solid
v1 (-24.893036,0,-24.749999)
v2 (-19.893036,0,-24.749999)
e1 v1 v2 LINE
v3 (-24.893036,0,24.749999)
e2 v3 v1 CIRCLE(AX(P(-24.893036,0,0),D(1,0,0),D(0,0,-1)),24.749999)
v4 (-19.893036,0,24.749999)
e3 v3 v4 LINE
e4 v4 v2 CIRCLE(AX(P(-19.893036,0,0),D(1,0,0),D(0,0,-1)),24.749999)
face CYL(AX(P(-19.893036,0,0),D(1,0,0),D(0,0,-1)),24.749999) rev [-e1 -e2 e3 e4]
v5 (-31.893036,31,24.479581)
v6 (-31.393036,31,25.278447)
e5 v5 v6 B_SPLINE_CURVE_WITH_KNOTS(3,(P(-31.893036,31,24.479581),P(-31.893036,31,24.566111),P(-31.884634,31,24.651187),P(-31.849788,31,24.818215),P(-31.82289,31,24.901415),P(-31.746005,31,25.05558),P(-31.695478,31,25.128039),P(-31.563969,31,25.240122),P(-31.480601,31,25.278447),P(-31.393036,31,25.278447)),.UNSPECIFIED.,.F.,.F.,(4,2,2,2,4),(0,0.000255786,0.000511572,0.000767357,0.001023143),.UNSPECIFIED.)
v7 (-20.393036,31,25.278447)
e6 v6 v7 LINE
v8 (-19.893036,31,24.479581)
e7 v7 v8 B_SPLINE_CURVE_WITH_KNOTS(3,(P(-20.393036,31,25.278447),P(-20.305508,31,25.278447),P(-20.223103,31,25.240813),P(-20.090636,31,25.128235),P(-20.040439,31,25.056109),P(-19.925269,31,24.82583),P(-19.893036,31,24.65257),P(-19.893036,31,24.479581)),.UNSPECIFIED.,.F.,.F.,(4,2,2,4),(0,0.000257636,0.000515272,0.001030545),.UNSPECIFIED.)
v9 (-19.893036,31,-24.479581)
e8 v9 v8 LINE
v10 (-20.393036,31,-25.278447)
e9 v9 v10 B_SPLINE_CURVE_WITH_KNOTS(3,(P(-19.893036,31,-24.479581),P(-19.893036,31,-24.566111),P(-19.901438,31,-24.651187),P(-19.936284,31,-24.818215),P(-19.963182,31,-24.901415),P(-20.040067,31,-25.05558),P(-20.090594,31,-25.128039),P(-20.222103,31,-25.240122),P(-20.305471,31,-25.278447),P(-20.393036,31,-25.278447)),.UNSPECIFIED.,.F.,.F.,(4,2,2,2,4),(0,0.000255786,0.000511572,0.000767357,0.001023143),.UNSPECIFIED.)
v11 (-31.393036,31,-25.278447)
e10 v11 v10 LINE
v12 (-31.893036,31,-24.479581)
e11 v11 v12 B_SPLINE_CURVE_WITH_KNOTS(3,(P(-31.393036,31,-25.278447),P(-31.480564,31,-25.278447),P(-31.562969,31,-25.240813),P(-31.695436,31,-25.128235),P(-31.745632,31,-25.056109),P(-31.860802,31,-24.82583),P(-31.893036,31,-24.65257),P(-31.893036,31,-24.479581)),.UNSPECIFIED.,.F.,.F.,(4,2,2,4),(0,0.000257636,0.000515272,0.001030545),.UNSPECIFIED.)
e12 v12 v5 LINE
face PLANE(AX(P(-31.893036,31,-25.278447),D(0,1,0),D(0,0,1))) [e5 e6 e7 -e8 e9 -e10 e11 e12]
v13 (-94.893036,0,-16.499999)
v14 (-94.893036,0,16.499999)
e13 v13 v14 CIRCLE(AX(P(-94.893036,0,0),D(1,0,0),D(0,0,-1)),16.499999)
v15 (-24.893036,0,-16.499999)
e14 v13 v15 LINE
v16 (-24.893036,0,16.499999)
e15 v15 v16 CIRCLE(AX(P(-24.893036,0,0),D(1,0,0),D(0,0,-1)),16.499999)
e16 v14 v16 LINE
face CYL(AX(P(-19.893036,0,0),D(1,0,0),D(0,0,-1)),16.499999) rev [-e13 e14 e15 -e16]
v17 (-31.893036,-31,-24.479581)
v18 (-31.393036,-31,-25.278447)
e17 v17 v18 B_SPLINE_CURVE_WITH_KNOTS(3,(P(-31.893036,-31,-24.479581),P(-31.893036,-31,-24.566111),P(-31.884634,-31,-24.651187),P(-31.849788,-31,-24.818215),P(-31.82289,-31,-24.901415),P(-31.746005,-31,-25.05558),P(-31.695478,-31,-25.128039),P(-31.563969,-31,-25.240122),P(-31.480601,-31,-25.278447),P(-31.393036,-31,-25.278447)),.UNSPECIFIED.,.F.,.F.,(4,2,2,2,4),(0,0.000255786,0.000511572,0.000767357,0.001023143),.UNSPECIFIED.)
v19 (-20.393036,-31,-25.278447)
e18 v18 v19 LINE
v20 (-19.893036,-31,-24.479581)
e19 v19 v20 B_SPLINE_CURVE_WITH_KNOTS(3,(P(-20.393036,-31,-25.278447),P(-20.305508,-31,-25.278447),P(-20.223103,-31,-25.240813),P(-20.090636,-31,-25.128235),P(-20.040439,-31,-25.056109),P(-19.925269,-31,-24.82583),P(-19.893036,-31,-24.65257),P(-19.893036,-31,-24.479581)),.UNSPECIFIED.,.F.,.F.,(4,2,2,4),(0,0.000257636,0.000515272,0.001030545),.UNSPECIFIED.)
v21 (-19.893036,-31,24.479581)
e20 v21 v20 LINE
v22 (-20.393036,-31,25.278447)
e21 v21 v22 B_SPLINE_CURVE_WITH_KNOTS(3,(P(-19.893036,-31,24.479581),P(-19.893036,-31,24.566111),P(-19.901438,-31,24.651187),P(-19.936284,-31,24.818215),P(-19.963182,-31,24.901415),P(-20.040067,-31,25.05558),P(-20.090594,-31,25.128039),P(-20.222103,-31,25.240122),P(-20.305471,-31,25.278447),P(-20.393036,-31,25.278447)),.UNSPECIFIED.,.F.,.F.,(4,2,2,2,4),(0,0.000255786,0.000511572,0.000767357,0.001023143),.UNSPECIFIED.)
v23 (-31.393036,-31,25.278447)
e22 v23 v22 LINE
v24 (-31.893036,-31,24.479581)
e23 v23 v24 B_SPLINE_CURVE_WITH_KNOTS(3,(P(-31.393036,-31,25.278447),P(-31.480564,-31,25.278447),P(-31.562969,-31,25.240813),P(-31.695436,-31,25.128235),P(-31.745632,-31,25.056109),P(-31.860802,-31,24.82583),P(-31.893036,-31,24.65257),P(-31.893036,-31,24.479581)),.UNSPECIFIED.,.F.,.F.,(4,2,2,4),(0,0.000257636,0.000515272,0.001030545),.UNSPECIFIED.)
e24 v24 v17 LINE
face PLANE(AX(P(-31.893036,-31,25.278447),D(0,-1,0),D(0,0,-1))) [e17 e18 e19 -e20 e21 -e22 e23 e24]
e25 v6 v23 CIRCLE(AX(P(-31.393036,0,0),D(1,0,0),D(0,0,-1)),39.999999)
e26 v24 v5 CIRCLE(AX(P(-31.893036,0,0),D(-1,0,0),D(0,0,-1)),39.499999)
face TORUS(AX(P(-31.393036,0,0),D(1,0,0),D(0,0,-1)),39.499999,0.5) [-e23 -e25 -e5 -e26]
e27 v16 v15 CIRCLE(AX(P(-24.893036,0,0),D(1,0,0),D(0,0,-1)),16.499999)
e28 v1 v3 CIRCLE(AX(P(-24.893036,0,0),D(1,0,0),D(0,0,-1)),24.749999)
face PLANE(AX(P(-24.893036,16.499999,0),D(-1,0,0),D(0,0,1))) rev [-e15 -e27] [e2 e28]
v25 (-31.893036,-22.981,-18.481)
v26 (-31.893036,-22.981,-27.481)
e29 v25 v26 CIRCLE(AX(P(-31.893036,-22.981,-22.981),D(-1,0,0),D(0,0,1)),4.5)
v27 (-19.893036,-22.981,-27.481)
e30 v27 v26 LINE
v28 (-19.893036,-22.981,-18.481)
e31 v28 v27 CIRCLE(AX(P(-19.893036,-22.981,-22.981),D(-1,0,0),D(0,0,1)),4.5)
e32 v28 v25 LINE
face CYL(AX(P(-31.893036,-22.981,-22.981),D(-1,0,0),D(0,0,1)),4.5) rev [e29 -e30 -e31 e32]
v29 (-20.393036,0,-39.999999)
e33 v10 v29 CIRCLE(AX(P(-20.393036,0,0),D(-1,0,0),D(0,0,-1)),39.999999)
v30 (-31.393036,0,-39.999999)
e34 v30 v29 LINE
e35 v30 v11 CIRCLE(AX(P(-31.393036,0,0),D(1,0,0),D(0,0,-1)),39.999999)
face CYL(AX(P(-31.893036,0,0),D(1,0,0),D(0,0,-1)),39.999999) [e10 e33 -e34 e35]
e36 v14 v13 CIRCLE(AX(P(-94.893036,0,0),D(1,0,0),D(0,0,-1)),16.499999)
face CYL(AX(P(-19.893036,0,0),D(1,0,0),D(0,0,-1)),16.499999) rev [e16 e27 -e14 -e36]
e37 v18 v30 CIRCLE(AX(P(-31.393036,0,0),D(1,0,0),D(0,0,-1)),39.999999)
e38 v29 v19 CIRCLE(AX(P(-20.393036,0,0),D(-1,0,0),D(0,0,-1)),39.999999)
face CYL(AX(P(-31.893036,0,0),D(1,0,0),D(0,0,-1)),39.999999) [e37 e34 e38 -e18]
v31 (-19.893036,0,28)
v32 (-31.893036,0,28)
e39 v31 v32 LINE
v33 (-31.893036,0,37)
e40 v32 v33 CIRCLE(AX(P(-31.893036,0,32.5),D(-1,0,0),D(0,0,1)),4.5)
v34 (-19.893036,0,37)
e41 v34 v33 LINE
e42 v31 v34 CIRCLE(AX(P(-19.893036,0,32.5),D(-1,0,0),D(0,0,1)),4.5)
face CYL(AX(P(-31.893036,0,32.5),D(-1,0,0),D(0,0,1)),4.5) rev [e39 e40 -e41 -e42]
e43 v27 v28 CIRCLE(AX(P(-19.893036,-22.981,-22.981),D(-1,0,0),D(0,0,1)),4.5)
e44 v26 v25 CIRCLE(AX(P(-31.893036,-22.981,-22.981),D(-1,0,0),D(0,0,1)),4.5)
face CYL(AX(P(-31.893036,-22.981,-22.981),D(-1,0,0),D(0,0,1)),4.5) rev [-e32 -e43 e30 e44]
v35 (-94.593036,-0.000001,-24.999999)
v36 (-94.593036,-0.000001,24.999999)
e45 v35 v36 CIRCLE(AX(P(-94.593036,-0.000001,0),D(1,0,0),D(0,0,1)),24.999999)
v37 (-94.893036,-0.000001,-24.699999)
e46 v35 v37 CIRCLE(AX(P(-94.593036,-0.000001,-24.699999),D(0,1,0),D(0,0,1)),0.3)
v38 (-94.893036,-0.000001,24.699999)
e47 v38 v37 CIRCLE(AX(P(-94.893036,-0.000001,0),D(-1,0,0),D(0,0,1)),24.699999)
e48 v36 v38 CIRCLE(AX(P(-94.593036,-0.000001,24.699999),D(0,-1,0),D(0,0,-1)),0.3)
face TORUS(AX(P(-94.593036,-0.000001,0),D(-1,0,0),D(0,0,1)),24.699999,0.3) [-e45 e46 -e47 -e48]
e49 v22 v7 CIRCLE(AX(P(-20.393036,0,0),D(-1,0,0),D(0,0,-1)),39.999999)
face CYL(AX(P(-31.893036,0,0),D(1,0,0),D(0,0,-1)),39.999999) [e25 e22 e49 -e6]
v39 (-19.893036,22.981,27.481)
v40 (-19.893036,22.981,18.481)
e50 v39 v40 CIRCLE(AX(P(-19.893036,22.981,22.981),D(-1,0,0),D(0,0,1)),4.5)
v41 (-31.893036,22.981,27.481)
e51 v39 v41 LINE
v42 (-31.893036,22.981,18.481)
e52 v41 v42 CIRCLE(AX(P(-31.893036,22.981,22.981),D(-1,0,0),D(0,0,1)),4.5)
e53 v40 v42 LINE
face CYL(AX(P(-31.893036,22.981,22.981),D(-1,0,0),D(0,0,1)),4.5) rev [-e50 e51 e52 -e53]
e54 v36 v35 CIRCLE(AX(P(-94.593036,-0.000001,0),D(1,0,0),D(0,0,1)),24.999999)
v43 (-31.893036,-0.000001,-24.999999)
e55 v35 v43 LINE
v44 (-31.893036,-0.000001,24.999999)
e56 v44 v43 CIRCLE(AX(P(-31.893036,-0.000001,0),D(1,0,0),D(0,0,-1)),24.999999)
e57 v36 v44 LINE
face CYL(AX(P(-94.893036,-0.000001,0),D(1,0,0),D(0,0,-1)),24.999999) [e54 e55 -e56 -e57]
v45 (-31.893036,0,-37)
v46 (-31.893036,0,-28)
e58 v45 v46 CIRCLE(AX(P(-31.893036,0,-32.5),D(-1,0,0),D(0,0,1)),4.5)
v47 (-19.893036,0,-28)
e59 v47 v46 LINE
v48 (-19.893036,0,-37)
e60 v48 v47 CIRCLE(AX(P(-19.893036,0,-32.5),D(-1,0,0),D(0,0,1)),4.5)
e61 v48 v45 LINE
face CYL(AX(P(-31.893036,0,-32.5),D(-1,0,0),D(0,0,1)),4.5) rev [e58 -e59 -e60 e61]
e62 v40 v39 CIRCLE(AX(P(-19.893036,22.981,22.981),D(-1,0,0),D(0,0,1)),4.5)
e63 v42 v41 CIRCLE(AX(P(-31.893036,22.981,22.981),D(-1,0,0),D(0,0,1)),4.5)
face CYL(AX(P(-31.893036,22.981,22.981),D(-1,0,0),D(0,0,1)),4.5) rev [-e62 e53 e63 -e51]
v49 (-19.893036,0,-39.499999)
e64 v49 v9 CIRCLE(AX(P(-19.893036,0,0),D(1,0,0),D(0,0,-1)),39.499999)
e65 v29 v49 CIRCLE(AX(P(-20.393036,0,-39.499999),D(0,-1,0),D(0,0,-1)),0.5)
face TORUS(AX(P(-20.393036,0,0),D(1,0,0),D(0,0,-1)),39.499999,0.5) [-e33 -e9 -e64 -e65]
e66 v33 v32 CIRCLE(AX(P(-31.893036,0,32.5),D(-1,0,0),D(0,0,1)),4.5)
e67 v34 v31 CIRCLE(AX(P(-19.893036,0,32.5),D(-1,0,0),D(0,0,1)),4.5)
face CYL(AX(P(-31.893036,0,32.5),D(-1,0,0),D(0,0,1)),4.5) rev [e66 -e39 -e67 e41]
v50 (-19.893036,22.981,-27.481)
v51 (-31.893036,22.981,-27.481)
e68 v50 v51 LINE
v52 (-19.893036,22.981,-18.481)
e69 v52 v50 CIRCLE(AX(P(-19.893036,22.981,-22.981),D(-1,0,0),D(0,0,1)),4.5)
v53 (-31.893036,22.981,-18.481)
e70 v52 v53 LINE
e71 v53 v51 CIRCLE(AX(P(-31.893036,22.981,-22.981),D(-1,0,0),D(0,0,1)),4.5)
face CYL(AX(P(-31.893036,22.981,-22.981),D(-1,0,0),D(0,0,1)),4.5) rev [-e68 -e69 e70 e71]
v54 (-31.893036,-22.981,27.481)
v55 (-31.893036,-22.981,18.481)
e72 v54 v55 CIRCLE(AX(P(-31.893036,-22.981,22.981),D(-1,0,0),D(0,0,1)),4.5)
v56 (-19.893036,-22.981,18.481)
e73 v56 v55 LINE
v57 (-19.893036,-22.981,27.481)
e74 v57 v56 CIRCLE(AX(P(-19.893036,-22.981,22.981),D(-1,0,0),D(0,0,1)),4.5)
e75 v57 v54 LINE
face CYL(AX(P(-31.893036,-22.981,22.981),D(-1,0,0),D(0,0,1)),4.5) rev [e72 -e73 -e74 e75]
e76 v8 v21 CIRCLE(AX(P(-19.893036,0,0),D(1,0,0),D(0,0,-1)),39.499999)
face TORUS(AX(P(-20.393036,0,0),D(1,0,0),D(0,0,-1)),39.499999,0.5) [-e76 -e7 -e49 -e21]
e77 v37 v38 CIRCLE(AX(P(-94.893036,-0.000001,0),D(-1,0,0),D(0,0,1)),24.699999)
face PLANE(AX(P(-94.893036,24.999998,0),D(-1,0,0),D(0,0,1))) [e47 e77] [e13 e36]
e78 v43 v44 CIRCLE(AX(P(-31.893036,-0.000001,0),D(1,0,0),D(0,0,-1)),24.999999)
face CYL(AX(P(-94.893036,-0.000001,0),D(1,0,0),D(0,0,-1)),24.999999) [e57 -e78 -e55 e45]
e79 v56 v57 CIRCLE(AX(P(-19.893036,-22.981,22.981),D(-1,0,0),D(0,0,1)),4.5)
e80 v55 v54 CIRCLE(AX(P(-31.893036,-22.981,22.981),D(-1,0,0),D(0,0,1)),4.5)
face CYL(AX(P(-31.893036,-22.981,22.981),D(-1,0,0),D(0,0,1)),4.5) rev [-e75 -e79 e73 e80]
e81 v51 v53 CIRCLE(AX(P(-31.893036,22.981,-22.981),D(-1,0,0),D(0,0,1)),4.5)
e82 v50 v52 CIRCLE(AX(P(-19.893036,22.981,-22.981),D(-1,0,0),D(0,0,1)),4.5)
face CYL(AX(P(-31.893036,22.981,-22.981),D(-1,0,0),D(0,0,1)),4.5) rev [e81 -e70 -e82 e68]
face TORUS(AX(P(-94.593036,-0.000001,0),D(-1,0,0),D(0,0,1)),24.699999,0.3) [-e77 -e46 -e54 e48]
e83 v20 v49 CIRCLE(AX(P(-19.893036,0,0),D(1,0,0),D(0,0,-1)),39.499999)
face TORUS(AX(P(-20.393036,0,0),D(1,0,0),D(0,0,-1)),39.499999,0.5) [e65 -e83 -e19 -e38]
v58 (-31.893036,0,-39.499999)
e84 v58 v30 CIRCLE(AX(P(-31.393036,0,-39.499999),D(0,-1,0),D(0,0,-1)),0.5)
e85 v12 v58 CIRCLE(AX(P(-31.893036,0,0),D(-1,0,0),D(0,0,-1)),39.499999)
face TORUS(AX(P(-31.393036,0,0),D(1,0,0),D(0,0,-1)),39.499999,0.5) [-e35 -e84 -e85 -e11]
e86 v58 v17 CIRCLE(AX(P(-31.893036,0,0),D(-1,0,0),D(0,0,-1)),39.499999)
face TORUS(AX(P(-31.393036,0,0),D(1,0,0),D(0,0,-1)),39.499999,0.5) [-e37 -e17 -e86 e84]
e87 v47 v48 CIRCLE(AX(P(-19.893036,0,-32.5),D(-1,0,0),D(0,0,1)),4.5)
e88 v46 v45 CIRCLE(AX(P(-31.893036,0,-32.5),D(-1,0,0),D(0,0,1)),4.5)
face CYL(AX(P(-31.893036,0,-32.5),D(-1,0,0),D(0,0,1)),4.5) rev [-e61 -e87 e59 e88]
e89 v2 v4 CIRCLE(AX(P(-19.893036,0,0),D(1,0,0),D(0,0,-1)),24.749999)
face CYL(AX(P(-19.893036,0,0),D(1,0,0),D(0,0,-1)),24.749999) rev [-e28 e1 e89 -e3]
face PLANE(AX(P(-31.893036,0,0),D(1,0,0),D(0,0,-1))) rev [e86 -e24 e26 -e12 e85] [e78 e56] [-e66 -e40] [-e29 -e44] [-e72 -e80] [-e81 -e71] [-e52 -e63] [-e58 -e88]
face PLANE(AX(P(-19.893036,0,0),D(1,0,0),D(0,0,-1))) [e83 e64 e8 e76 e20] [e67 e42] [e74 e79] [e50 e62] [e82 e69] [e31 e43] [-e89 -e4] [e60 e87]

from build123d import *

# Parameters (mm, degrees)
EXTRUDE_1_DEPTH               = 11.999999998
SKETCH_2_W                    = 63.000000153
SKETCH_2_H                    = 24.999999254
HOLE_WIZARD_9_0_9_1_D         = 9
HOLE_WIZARD_M30_1_D           = 32.999998421
HOLE_WIZARD_M30_1_CBORE_D     = 49.499997436
HOLE_WIZARD_M30_1_CBORE_DEPTH = 5
FILLET_1_R                    = 0.3
FILLET_2_R                    = 0.5


with BuildPart() as part:
    # 草图1 → 凸台-拉伸1 (new body)
    with BuildSketch(Plane(origin=(-19.893035878, 0, 0), x_dir=(0, 0, -1), z_dir=(1, 0, 0))):
        with BuildLine():
            Line((25.278447364, 30.999999739), (-25.278447364, 30.999999739))
            ThreePointArc((-25.278447364, 30.999999739), (-39.999998764, -2.61e-07), (-25.278447364, -31.000000261))
            Line((-25.278447364, -31.000000261), (25.278447364, -31.000000261))
            ThreePointArc((25.278447364, -31.000000261), (39.999998764, -2.61e-07), (25.278447364, 30.999999739))
        make_face()
    extrude(amount=-EXTRUDE_1_DEPTH)

    # 草图2 → 旋转1 (revolve)
    with BuildSketch(Plane.XY, mode=Mode.PRIVATE) as revolve_1_sk:
        with Locations((-63.393035954, 12.499998381)):
            Rectangle(SKETCH_2_W, SKETCH_2_H)
    revolve(revolve_1_sk.sketch.rotate(Axis((-94.89303603, -1.246e-06, 0), (1, 0, 0)), 270), axis=Axis((-94.89303603, -1.246e-06, 0), (1, 0, 0)))

    # Ø9.0 (9) 直径孔1 (through all)
    with Locations(Plane.ZY.offset(31.893035877)):
        with Locations((22.981, 22.980999581), (22.981, -22.981000419), (-22.981, -22.981000419), (-22.981, 22.980999581), (32.5, -4.19e-07), (-32.5, -4.19e-07)):
            Hole(HOLE_WIZARD_9_0_9_1_D / 2)

    # M30 六角头螺栓的柱形沉头孔1 (through all)
    with Locations(Plane(origin=(-19.893035878, 0, 0), x_dir=(0, 0, -1), z_dir=(1, 0, 0))):
        with Locations((0, -2.61e-07)):
            CounterBoreHole(HOLE_WIZARD_M30_1_D / 2, HOLE_WIZARD_M30_1_CBORE_D / 2, HOLE_WIZARD_M30_1_CBORE_DEPTH)

    # 圆角1
    fillet_1_edges = [part.edges().sort_by_distance(p)[0] for p in [
        (-94.89303603, -1.246e-06, 24.999999255),
    ]]
    fillet(fillet_1_edges, radius=FILLET_1_R)

    # 圆角2
    fillet_2_edges = [part.edges().sort_by_distance(p)[0] for p in [
        (-31.893035877, -2.61e-07, 39.999998764),
        (-31.893035877, -2.61e-07, -39.999998764),
        (-19.893035878, -2.61e-07, 39.999998764),
        (-19.893035878, -2.61e-07, -39.999998764),
    ]]
    fillet(fillet_2_edges, radius=FILLET_2_R)


solid = part.part
